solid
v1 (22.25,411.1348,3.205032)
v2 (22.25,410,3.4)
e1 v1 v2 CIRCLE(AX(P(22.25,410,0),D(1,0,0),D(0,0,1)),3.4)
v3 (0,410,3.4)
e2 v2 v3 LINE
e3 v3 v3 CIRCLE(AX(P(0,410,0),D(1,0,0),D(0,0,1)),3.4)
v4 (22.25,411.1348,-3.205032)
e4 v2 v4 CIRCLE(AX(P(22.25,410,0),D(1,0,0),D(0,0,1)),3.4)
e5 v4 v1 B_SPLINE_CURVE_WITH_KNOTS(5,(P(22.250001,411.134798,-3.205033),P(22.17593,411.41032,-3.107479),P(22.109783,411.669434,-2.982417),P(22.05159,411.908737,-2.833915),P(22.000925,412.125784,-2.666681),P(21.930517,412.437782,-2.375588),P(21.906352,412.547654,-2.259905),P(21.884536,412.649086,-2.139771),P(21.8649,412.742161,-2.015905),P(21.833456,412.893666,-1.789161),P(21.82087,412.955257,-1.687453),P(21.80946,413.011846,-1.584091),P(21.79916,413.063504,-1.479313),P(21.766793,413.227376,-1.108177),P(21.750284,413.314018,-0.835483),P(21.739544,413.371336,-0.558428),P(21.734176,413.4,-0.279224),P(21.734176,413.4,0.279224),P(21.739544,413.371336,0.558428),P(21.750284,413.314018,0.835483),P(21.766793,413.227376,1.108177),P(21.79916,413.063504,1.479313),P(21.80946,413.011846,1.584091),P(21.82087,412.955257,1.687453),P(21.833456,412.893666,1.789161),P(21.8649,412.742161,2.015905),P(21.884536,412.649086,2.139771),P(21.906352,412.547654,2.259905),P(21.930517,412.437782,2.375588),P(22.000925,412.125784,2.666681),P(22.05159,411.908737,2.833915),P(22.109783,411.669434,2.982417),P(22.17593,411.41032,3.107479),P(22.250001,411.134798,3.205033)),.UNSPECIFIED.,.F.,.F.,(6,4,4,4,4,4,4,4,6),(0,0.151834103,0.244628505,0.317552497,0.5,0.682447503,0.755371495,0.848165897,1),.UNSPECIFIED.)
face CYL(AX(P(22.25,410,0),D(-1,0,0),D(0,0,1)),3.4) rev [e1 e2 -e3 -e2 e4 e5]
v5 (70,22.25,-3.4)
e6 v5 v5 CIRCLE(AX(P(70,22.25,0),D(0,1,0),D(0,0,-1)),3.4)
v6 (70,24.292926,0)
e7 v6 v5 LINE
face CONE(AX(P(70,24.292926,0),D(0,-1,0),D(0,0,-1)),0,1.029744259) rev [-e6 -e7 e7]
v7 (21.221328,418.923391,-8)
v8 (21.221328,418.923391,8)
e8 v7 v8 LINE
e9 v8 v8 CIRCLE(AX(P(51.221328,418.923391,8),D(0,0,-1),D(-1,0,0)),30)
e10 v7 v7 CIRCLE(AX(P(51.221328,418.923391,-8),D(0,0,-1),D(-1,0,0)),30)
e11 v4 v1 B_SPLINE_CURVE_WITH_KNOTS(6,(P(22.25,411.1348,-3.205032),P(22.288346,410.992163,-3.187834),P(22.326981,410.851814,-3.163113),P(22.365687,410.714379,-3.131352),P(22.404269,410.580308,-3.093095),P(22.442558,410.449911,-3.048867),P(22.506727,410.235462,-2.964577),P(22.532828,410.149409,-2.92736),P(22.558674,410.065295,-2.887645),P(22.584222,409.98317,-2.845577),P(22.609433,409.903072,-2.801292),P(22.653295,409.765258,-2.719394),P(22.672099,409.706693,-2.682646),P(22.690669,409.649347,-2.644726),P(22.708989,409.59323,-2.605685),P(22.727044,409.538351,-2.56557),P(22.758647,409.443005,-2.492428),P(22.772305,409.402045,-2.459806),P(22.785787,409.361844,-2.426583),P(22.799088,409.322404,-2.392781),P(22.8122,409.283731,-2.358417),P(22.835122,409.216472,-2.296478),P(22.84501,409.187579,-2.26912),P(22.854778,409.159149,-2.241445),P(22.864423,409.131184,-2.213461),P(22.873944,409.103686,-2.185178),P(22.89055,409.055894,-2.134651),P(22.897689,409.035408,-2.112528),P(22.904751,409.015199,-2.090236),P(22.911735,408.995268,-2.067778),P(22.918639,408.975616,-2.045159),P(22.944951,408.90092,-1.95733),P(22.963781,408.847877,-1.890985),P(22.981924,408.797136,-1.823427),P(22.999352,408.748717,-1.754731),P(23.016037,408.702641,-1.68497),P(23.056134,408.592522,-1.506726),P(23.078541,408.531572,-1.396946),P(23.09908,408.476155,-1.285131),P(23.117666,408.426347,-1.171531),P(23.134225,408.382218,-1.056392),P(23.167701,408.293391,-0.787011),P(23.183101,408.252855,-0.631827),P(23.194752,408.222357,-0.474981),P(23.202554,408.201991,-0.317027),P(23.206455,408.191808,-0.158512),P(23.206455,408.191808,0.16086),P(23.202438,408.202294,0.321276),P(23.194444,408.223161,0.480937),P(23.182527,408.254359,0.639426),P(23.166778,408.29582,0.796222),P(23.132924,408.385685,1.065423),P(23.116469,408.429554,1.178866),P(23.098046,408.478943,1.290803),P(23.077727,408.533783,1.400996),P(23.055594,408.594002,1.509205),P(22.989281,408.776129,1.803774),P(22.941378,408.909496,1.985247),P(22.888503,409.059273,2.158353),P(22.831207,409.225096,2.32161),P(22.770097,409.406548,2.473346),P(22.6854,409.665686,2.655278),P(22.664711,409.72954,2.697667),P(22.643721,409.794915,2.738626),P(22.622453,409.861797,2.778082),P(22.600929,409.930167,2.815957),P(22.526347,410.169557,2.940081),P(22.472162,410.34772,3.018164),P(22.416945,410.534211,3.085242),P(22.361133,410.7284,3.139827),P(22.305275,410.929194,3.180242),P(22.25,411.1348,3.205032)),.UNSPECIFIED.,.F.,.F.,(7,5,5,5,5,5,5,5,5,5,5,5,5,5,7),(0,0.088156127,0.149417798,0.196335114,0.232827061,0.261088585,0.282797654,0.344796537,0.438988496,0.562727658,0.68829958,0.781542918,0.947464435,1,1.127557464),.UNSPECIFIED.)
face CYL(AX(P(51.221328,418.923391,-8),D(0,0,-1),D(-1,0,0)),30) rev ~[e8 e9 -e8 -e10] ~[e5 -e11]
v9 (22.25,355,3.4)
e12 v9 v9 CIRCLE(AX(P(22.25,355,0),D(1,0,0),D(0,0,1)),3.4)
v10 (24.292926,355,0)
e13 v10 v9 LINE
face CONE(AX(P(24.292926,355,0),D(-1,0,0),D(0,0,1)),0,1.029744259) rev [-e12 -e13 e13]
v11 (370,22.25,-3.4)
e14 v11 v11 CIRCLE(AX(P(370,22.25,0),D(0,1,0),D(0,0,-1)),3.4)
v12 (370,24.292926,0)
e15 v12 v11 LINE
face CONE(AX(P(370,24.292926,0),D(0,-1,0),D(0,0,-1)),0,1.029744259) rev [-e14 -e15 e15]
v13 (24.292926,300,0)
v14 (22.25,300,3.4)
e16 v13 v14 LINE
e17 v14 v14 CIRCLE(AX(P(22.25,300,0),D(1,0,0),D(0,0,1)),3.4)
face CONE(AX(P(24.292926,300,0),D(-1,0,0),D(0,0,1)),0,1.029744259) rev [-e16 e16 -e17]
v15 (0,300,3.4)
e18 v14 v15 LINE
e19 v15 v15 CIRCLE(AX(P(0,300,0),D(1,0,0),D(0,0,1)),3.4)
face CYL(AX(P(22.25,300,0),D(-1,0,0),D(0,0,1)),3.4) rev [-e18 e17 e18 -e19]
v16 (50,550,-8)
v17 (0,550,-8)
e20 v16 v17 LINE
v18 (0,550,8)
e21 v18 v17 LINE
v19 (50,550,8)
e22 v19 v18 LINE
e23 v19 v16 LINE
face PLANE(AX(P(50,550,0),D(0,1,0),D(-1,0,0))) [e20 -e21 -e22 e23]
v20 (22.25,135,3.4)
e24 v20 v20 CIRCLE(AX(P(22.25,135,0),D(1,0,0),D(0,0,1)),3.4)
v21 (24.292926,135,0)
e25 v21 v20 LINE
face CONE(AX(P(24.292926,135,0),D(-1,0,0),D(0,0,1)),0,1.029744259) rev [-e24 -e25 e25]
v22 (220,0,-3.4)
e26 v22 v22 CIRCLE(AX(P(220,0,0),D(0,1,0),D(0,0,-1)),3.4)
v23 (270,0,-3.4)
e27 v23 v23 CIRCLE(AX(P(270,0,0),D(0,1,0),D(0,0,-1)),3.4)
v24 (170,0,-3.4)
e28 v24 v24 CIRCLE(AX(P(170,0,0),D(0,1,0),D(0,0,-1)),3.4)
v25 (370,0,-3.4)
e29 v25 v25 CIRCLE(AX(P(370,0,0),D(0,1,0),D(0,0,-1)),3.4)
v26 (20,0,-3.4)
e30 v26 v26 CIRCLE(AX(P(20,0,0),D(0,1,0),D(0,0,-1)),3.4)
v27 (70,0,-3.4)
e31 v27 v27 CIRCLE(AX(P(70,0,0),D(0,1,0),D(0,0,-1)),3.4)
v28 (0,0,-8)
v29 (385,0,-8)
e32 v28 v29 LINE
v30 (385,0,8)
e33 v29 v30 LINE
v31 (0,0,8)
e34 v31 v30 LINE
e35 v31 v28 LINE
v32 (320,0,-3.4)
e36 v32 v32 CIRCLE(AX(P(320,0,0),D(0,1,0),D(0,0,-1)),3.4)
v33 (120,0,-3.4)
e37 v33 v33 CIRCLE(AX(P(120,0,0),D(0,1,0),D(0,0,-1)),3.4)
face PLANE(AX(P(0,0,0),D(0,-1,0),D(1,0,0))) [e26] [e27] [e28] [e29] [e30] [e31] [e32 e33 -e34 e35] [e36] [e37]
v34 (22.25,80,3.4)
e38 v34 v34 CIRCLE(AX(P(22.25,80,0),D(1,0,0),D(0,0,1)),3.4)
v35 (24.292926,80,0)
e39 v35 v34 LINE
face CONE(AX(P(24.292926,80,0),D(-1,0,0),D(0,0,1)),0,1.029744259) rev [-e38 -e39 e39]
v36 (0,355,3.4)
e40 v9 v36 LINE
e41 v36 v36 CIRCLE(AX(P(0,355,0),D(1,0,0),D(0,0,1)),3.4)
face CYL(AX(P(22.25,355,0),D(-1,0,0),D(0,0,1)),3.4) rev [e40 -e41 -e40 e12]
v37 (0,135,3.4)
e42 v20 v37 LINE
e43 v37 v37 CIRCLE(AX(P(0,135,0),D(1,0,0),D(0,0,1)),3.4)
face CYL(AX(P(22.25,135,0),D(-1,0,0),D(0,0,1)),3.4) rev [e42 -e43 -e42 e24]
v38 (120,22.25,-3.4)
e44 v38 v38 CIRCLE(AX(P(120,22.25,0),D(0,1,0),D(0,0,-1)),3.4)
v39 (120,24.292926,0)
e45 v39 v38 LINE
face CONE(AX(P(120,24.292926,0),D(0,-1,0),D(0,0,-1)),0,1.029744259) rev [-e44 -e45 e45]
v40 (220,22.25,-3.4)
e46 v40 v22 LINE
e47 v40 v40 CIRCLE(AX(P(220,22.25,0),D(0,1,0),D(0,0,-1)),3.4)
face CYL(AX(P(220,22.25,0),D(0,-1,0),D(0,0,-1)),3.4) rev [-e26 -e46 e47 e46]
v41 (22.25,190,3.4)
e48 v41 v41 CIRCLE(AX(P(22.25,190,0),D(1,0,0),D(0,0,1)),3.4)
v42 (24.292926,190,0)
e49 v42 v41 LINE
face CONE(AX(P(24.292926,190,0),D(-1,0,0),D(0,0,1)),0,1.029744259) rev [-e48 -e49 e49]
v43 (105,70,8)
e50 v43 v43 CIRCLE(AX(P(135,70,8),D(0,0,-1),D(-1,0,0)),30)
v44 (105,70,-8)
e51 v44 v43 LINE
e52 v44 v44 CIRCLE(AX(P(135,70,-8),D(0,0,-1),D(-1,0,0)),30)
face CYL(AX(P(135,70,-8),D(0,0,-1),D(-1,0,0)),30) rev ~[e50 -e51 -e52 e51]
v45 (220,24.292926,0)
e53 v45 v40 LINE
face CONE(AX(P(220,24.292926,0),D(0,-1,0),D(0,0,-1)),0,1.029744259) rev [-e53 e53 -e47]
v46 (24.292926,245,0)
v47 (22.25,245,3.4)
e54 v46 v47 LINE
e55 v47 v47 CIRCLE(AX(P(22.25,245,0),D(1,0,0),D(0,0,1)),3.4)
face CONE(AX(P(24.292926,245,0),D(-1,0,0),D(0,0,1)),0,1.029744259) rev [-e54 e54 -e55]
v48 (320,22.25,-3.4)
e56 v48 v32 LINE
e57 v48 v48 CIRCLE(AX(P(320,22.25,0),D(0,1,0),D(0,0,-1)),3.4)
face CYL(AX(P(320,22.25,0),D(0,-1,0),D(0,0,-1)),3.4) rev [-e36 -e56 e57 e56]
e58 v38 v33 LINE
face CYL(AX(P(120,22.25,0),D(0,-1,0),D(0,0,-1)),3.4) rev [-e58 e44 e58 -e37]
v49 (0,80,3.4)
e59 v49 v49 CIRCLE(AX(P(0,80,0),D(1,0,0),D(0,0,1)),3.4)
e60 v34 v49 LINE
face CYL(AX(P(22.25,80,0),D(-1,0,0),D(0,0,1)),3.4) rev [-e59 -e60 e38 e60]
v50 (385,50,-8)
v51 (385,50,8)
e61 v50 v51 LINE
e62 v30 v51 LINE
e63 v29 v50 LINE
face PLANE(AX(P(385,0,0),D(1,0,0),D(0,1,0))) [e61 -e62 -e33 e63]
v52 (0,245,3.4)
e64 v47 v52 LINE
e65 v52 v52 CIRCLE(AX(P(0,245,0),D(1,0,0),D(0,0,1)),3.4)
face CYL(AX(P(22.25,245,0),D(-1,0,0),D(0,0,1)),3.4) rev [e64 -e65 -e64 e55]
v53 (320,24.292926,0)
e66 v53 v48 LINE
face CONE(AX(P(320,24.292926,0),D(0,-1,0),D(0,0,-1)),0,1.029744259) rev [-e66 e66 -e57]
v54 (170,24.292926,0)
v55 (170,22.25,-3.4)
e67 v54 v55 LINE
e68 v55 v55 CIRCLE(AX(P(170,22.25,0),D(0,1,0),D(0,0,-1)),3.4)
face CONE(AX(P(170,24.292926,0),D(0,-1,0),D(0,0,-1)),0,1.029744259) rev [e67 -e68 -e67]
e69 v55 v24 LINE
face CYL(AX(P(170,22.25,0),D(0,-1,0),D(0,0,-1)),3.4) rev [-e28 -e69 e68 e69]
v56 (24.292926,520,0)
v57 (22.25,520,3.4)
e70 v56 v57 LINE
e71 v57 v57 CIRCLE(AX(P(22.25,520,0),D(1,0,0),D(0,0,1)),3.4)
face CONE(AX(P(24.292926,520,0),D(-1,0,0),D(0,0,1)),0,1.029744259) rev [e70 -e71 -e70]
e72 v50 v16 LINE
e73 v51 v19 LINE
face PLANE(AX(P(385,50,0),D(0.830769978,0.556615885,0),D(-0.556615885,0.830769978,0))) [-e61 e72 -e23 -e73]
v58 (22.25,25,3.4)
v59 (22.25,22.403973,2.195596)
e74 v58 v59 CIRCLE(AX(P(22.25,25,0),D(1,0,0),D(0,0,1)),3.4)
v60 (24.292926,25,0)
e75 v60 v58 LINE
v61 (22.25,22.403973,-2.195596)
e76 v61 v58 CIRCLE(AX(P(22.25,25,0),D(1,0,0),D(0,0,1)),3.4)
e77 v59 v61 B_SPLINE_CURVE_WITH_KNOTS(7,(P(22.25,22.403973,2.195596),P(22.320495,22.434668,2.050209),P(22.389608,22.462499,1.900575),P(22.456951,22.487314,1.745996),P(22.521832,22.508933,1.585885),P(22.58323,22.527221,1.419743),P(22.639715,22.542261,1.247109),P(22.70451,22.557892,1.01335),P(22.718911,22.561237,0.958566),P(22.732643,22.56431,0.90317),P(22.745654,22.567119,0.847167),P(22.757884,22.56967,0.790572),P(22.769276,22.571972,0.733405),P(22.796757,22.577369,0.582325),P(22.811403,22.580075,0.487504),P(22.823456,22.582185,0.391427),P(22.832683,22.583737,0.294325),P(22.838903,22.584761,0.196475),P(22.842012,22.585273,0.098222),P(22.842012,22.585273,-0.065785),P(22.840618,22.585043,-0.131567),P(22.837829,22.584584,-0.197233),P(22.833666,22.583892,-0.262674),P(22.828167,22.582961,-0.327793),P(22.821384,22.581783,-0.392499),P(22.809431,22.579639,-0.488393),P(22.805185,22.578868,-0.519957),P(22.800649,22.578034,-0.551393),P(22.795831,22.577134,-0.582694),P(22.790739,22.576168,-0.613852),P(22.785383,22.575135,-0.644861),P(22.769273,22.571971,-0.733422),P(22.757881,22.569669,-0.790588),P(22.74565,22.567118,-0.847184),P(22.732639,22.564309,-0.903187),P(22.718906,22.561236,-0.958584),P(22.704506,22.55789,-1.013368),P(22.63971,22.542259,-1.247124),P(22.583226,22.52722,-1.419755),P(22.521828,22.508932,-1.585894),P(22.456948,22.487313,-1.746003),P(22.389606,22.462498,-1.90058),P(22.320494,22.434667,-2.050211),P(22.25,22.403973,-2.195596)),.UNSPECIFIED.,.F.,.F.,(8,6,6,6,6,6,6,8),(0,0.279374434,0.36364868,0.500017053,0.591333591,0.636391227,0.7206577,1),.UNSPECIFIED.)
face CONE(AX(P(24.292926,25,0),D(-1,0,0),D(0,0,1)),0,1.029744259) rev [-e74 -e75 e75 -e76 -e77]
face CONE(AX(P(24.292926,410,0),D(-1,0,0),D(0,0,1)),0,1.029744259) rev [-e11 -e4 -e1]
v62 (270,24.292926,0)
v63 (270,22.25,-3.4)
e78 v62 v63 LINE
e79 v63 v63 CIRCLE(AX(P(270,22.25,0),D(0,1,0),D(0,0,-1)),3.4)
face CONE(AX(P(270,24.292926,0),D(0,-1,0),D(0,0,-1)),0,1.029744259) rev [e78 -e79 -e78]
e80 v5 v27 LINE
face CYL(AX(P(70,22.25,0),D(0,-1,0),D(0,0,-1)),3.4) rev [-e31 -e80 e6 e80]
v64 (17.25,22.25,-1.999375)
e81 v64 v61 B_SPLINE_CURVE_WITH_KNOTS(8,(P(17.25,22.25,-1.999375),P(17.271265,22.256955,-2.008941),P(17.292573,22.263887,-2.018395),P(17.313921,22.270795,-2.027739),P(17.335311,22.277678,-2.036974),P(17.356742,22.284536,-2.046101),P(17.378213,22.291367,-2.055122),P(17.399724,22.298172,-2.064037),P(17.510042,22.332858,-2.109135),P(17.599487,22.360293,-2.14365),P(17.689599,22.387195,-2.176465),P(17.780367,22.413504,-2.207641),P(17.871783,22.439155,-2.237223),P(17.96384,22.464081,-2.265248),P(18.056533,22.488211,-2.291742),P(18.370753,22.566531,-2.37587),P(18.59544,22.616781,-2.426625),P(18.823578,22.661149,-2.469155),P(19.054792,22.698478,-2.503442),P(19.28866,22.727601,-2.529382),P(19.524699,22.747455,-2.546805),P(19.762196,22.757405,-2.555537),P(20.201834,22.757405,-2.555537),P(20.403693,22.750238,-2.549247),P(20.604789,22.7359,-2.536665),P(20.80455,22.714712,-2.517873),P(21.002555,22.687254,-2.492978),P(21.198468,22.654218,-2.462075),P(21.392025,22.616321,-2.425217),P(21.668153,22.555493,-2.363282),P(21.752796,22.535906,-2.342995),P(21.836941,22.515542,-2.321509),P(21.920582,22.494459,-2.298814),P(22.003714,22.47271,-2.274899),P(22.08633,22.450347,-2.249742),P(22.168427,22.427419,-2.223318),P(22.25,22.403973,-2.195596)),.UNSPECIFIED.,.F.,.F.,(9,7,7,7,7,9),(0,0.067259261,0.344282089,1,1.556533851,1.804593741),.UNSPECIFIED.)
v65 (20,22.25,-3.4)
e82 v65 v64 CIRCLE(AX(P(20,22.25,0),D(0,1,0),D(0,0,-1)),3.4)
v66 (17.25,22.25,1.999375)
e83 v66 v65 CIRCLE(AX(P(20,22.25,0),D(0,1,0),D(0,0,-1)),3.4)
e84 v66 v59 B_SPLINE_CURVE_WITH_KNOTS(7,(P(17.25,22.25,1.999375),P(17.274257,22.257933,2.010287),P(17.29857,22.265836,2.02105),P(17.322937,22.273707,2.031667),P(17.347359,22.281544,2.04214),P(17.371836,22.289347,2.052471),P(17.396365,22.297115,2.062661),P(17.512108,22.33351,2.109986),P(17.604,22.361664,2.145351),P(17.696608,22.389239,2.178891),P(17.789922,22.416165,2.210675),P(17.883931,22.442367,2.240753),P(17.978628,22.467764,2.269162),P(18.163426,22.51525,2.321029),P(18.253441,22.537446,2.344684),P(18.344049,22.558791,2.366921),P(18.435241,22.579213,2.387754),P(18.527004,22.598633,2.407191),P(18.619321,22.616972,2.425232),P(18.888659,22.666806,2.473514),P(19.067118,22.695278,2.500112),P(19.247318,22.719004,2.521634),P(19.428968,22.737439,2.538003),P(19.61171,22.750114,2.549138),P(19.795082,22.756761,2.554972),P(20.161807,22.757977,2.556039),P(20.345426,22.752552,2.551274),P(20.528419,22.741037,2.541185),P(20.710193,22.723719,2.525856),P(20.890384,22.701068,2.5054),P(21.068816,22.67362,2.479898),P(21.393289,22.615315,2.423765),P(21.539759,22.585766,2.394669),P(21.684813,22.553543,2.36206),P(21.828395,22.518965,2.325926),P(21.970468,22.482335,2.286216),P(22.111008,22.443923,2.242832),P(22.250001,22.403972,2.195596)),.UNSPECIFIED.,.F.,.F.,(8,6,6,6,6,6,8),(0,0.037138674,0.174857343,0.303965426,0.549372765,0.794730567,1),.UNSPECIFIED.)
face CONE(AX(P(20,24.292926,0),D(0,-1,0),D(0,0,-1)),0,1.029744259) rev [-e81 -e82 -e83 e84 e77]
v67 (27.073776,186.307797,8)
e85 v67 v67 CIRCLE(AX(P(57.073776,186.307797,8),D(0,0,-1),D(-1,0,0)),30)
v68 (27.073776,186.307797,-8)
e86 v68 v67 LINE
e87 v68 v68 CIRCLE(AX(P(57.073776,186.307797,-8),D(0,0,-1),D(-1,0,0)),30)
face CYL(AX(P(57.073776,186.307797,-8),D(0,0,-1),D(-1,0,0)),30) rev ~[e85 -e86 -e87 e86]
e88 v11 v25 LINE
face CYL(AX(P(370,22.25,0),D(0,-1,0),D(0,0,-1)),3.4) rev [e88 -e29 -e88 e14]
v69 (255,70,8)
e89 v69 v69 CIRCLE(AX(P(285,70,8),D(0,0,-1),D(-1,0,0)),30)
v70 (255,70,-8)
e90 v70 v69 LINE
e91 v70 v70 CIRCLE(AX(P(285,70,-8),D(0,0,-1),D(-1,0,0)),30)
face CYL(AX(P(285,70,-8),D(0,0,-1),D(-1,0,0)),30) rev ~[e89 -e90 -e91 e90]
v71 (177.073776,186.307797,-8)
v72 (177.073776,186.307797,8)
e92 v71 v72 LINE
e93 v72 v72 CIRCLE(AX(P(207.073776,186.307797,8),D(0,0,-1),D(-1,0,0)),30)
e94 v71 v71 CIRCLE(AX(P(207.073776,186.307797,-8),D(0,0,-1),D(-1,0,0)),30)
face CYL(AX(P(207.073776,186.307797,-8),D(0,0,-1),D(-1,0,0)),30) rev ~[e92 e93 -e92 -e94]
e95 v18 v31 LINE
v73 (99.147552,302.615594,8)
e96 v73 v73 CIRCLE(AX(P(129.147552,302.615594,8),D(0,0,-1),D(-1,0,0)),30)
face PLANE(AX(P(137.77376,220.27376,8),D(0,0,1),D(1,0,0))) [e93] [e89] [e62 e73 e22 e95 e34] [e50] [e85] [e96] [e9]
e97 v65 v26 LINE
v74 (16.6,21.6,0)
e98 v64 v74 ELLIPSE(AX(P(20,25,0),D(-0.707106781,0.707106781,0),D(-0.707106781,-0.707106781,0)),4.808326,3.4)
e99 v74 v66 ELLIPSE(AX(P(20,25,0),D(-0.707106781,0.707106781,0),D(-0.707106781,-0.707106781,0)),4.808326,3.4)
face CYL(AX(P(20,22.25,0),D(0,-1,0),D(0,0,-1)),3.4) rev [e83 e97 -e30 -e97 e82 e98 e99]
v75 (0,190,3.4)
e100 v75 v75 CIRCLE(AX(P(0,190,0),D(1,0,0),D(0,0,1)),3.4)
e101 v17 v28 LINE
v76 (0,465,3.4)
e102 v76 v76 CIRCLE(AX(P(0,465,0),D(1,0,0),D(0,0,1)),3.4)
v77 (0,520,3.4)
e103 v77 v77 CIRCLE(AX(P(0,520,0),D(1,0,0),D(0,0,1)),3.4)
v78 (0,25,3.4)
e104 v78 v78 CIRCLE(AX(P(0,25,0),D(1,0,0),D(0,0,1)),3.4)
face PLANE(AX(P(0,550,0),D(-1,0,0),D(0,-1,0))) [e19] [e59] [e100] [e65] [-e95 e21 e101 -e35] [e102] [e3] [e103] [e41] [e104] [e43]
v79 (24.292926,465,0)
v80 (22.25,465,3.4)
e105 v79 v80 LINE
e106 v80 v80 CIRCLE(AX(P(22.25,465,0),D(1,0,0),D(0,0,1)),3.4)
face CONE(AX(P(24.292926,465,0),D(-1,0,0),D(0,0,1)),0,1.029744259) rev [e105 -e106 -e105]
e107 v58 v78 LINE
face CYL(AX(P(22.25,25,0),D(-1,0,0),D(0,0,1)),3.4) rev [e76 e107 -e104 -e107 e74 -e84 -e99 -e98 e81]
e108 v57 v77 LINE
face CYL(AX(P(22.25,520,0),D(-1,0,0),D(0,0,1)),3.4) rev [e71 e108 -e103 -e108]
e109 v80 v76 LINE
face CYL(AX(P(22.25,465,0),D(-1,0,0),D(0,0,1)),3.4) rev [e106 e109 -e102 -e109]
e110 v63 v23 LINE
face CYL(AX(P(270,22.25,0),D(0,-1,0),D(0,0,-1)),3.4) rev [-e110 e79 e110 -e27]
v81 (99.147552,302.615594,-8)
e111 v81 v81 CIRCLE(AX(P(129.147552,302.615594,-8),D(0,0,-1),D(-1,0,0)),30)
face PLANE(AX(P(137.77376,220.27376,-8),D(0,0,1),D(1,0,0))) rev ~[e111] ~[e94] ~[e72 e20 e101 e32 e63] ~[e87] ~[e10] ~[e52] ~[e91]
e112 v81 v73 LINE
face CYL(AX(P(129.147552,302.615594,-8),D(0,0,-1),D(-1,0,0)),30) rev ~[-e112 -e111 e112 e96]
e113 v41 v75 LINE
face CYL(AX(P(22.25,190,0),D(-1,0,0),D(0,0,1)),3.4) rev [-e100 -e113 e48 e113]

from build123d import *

# Parameters (mm, degrees)
EXTRUDE_1_DEPTH        = 8
PATTERN_LINEAR_1_COUNT = 10
PATTERN_LINEAR_1_PITCH = 55
PATTERN_LINEAR_2_COUNT = 8
PATTERN_LINEAR_2_PITCH = 50
SKETCH_6_R             = 30
CUT_EXTRUDE_1_DEPTH    = 672.551189411


with BuildPart() as part:
    # 草图1 → 凸台-拉伸1 (new, symmetric)
    with BuildSketch(Plane.XY):
        Polygon((0, 0), (385, 0), (385, 50), (50, 550), (0, 550), align=None)
    extrude(amount=EXTRUDE_1_DEPTH, both=True)

    # 草图3 → M8 螺纹孔1 (revolve, cut)
    with BuildSketch(Plane.ZX.offset(520)):
        Polygon((0, 0), (0, 24.292926105), (3.4, 22.25), (3.4, 0), align=None)
    hole_wizard_m8_1 = revolve(axis=Axis((-6.35, 520, 0), (1, 0, 0)), mode=Mode.SUBTRACT)

    # 阵列(线性)1: M8 螺纹孔1 ×10
    with Locations(*[(0, -i * PATTERN_LINEAR_1_PITCH, 0) for i in range(1, PATTERN_LINEAR_1_COUNT)]):
        add(hole_wizard_m8_1, mode=Mode.SUBTRACT)

    # 草图5 → M8 螺纹孔2 (revolve, cut)
    with BuildSketch(Plane(origin=(20, 0, 0), x_dir=(0, 0, -1), z_dir=(1, 0, 0))):
        Polygon((0, 0), (0, 24.292926105), (3.4, 22.25), (3.4, 0), align=None)
    hole_wizard_m8_2 = revolve(axis=Axis((20, -6.35, 0), (0, 1, 0)), mode=Mode.SUBTRACT)

    # 阵列(线性)2: M8 螺纹孔2 ×8
    with Locations(*[(i * PATTERN_LINEAR_2_PITCH, 0, 0) for i in range(1, PATTERN_LINEAR_2_COUNT)]):
        add(hole_wizard_m8_2, mode=Mode.SUBTRACT)

    # 草图6 → 切除-拉伸1 (cut, through all)
    with BuildSketch(Plane(origin=(0, 0, -8), x_dir=(-1, 0, 0), z_dir=(0, 0, -1))):
        with Locations((-285, 70)):
            Circle(SKETCH_6_R)
        with Locations((-129.147552133, 302.615593832)):
            Circle(SKETCH_6_R)
        with Locations((-207.073776066, 186.307796916)):
            Circle(SKETCH_6_R)
        with Locations((-135, 70)):
            Circle(SKETCH_6_R)
        with Locations((-51.221328199, 418.923390748)):
            Circle(SKETCH_6_R)
        with Locations((-57.073776066, 186.307796916)):
            Circle(SKETCH_6_R)
    extrude(amount=-CUT_EXTRUDE_1_DEPTH, mode=Mode.SUBTRACT)


solid = part.part
